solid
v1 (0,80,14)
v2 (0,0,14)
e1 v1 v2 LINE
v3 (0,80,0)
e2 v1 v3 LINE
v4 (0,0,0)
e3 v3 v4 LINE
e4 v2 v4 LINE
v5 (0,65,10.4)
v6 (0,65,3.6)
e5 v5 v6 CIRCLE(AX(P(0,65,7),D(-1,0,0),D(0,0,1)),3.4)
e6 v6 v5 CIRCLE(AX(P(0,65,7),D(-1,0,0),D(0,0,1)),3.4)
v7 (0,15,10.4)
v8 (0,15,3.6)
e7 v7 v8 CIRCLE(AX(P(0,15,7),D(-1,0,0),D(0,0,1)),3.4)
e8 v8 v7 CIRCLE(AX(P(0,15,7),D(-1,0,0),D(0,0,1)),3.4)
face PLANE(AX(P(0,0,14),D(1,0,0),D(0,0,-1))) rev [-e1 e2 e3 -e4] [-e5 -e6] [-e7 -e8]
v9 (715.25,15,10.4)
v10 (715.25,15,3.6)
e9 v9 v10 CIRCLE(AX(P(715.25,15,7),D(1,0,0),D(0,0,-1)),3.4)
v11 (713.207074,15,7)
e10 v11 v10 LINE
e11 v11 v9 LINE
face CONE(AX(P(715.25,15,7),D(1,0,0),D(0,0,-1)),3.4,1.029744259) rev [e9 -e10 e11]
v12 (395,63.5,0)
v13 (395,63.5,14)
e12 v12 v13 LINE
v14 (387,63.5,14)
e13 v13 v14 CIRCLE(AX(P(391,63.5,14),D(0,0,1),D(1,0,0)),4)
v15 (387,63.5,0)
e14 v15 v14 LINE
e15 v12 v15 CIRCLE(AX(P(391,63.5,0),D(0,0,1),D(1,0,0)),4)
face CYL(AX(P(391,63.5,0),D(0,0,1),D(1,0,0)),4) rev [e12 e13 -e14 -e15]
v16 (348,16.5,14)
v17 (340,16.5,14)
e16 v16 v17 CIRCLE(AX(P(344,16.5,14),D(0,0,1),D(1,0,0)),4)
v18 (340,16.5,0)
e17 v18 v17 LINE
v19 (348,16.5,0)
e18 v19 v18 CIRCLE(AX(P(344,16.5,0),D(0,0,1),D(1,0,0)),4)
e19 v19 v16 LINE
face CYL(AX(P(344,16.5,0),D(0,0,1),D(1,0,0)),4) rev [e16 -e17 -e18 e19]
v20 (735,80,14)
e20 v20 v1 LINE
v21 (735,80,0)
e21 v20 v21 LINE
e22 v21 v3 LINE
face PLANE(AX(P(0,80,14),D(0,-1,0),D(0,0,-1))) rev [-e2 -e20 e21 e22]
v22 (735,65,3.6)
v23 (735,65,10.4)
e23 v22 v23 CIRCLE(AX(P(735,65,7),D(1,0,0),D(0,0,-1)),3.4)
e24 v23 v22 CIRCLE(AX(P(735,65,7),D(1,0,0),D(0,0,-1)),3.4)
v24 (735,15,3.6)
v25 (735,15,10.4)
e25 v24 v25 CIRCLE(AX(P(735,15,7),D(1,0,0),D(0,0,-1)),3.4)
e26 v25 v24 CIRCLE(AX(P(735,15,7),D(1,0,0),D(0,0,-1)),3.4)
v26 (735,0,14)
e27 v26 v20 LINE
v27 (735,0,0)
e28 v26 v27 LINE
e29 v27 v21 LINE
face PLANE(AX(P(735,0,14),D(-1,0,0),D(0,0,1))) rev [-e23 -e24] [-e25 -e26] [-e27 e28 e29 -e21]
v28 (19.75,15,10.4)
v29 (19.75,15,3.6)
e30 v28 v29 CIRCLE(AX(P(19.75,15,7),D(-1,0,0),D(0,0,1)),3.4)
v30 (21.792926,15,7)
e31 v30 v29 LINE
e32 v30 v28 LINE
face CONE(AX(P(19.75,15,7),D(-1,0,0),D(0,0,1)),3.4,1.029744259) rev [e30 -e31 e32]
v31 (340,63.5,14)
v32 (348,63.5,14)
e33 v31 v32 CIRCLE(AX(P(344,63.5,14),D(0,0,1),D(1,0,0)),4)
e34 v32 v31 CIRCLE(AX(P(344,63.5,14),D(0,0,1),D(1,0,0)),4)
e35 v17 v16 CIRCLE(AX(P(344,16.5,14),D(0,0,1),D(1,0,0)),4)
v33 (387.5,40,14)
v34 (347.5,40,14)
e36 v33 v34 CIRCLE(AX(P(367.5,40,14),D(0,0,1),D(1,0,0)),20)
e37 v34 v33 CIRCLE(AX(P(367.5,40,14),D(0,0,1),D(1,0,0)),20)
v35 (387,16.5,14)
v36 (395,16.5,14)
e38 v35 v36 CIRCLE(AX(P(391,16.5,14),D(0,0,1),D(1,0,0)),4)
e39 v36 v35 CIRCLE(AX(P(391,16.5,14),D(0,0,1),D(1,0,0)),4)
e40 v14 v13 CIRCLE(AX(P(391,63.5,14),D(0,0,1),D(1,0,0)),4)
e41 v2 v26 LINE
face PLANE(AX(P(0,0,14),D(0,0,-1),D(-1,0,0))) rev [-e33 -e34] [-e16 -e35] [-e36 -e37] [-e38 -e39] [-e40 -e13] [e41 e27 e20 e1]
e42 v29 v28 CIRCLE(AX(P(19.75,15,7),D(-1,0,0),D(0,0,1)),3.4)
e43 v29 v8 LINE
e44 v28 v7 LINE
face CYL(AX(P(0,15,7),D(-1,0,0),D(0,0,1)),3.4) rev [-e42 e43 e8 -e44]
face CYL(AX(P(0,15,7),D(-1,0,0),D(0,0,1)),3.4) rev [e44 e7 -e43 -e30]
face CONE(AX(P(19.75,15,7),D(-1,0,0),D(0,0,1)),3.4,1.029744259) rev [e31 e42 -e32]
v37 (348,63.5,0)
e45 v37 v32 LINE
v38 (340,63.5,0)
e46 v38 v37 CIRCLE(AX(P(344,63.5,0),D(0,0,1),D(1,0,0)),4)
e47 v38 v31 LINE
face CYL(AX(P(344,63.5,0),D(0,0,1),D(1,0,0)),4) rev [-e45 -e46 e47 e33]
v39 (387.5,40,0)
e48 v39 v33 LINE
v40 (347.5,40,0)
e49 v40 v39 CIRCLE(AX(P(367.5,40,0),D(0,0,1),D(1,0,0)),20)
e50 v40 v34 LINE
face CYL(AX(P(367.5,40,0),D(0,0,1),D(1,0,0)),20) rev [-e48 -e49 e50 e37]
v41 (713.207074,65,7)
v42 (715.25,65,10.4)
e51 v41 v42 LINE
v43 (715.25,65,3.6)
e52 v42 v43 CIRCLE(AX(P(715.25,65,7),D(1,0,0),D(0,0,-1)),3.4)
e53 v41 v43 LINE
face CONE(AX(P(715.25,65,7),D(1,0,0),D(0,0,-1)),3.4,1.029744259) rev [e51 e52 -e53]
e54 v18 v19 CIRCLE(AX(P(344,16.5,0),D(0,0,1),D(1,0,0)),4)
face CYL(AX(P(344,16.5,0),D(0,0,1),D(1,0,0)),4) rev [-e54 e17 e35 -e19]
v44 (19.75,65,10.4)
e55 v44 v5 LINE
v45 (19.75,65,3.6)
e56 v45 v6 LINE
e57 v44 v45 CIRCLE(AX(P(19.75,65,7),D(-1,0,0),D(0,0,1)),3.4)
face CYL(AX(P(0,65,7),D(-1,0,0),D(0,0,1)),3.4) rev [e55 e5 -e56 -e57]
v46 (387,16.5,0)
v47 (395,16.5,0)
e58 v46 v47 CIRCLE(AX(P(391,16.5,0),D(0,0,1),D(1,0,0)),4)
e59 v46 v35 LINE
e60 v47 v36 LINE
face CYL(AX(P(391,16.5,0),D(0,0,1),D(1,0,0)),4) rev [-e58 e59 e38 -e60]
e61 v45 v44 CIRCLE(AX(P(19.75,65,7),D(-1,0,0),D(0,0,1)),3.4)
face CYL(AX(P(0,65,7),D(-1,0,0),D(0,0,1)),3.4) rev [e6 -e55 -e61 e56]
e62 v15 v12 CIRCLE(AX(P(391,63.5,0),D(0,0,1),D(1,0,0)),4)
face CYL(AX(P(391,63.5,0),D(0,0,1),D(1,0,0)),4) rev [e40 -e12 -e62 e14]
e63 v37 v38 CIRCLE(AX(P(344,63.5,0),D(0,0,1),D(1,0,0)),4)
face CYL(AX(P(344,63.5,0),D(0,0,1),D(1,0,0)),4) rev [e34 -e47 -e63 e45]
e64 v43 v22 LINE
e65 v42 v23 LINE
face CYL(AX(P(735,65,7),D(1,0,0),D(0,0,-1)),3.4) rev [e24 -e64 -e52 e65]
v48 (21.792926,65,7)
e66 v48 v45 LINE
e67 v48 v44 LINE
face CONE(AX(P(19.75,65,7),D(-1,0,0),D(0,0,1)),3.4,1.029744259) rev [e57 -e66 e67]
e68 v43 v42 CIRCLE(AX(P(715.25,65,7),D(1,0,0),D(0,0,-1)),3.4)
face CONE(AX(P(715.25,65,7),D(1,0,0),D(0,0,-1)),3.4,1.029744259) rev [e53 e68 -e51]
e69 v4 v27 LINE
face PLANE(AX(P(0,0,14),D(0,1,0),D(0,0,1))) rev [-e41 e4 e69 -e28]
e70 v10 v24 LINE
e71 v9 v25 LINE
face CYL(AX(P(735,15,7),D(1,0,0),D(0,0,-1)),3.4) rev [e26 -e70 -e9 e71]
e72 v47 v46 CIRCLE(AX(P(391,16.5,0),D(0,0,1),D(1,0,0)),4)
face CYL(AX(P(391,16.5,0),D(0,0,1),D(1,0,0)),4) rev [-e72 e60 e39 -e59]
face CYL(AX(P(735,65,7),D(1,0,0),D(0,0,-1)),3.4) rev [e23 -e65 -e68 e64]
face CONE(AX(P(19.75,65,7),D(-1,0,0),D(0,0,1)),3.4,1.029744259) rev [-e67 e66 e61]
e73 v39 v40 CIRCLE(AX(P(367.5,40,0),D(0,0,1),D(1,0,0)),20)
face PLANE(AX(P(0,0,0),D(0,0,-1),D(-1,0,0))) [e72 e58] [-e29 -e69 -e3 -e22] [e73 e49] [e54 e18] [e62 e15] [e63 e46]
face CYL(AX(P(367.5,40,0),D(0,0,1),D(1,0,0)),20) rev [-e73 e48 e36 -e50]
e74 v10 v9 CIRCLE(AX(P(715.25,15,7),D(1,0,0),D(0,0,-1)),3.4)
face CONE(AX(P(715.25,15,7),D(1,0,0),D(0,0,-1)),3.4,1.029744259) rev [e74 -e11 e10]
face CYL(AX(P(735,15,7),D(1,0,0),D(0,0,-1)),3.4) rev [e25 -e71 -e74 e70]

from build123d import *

# Parameters (mm, degrees)
SKETCH1_W             = 735
SKETCH1_H             = 80
BOSS_EXTRUDE1_DEPTH   = 14
SKETCH2_R             = 4
SKETCH2_R_2           = 20
CUT_EXTRUDE1_DEPTH    = 14
M8_TAPPED_HOLE1_D     = 6.8
M8_TAPPED_HOLE1_DEPTH = 19.75
M8_TAPPED_HOLE1_TIP   = 2.042926105
M8_TAPPED_HOLE2_D     = 6.8
M8_TAPPED_HOLE2_DEPTH = 19.75
M8_TAPPED_HOLE2_TIP   = 2.042926105


with BuildPart() as part:
    # Sketch1 → Boss-Extrude1 (new body)
    with BuildSketch(Plane.XY):
        with Locations((367.5, 40)):
            Rectangle(SKETCH1_W, SKETCH1_H)
    extrude(amount=BOSS_EXTRUDE1_DEPTH)

    # Sketch2 → Cut-Extrude1 (cut)
    with BuildSketch(Plane.XY.offset(14)):
        with Locations((344, 63.5)):
            Circle(SKETCH2_R)
        with Locations((344, 16.5)):
            Circle(SKETCH2_R)
        with Locations((391, 16.5)):
            Circle(SKETCH2_R)
        with Locations((391, 63.5)):
            Circle(SKETCH2_R)
        with Locations((367.5, 40)):
            Circle(SKETCH2_R_2)
    extrude(amount=-CUT_EXTRUDE1_DEPTH, mode=Mode.SUBTRACT)

    # M8 Tapped Hole1
    with Locations(Plane(origin=(0, 65, 7), x_dir=(0, 0, -1), z_dir=(-1, 0, 0))):
        with Locations((0, 0), (0, 50)):
            Hole(M8_TAPPED_HOLE1_D / 2, depth=M8_TAPPED_HOLE1_DEPTH)
            with Locations((0, 0, -(M8_TAPPED_HOLE1_DEPTH + M8_TAPPED_HOLE1_TIP / 2))):  # 118° drill point
                Cone(0, M8_TAPPED_HOLE1_D / 2, M8_TAPPED_HOLE1_TIP, mode=Mode.SUBTRACT)

    # M8 Tapped Hole2
    with Locations(Plane(origin=(735, 15, 7), x_dir=(0, 0, 1), z_dir=(1, 0, 0))):
        with Locations((0, 0), (0, -50)):
            Hole(M8_TAPPED_HOLE2_D / 2, depth=M8_TAPPED_HOLE2_DEPTH)
            with Locations((0, 0, -(M8_TAPPED_HOLE2_DEPTH + M8_TAPPED_HOLE2_TIP / 2))):  # 118° drill point
                Cone(0, M8_TAPPED_HOLE2_D / 2, M8_TAPPED_HOLE2_TIP, mode=Mode.SUBTRACT)


solid = part.part
